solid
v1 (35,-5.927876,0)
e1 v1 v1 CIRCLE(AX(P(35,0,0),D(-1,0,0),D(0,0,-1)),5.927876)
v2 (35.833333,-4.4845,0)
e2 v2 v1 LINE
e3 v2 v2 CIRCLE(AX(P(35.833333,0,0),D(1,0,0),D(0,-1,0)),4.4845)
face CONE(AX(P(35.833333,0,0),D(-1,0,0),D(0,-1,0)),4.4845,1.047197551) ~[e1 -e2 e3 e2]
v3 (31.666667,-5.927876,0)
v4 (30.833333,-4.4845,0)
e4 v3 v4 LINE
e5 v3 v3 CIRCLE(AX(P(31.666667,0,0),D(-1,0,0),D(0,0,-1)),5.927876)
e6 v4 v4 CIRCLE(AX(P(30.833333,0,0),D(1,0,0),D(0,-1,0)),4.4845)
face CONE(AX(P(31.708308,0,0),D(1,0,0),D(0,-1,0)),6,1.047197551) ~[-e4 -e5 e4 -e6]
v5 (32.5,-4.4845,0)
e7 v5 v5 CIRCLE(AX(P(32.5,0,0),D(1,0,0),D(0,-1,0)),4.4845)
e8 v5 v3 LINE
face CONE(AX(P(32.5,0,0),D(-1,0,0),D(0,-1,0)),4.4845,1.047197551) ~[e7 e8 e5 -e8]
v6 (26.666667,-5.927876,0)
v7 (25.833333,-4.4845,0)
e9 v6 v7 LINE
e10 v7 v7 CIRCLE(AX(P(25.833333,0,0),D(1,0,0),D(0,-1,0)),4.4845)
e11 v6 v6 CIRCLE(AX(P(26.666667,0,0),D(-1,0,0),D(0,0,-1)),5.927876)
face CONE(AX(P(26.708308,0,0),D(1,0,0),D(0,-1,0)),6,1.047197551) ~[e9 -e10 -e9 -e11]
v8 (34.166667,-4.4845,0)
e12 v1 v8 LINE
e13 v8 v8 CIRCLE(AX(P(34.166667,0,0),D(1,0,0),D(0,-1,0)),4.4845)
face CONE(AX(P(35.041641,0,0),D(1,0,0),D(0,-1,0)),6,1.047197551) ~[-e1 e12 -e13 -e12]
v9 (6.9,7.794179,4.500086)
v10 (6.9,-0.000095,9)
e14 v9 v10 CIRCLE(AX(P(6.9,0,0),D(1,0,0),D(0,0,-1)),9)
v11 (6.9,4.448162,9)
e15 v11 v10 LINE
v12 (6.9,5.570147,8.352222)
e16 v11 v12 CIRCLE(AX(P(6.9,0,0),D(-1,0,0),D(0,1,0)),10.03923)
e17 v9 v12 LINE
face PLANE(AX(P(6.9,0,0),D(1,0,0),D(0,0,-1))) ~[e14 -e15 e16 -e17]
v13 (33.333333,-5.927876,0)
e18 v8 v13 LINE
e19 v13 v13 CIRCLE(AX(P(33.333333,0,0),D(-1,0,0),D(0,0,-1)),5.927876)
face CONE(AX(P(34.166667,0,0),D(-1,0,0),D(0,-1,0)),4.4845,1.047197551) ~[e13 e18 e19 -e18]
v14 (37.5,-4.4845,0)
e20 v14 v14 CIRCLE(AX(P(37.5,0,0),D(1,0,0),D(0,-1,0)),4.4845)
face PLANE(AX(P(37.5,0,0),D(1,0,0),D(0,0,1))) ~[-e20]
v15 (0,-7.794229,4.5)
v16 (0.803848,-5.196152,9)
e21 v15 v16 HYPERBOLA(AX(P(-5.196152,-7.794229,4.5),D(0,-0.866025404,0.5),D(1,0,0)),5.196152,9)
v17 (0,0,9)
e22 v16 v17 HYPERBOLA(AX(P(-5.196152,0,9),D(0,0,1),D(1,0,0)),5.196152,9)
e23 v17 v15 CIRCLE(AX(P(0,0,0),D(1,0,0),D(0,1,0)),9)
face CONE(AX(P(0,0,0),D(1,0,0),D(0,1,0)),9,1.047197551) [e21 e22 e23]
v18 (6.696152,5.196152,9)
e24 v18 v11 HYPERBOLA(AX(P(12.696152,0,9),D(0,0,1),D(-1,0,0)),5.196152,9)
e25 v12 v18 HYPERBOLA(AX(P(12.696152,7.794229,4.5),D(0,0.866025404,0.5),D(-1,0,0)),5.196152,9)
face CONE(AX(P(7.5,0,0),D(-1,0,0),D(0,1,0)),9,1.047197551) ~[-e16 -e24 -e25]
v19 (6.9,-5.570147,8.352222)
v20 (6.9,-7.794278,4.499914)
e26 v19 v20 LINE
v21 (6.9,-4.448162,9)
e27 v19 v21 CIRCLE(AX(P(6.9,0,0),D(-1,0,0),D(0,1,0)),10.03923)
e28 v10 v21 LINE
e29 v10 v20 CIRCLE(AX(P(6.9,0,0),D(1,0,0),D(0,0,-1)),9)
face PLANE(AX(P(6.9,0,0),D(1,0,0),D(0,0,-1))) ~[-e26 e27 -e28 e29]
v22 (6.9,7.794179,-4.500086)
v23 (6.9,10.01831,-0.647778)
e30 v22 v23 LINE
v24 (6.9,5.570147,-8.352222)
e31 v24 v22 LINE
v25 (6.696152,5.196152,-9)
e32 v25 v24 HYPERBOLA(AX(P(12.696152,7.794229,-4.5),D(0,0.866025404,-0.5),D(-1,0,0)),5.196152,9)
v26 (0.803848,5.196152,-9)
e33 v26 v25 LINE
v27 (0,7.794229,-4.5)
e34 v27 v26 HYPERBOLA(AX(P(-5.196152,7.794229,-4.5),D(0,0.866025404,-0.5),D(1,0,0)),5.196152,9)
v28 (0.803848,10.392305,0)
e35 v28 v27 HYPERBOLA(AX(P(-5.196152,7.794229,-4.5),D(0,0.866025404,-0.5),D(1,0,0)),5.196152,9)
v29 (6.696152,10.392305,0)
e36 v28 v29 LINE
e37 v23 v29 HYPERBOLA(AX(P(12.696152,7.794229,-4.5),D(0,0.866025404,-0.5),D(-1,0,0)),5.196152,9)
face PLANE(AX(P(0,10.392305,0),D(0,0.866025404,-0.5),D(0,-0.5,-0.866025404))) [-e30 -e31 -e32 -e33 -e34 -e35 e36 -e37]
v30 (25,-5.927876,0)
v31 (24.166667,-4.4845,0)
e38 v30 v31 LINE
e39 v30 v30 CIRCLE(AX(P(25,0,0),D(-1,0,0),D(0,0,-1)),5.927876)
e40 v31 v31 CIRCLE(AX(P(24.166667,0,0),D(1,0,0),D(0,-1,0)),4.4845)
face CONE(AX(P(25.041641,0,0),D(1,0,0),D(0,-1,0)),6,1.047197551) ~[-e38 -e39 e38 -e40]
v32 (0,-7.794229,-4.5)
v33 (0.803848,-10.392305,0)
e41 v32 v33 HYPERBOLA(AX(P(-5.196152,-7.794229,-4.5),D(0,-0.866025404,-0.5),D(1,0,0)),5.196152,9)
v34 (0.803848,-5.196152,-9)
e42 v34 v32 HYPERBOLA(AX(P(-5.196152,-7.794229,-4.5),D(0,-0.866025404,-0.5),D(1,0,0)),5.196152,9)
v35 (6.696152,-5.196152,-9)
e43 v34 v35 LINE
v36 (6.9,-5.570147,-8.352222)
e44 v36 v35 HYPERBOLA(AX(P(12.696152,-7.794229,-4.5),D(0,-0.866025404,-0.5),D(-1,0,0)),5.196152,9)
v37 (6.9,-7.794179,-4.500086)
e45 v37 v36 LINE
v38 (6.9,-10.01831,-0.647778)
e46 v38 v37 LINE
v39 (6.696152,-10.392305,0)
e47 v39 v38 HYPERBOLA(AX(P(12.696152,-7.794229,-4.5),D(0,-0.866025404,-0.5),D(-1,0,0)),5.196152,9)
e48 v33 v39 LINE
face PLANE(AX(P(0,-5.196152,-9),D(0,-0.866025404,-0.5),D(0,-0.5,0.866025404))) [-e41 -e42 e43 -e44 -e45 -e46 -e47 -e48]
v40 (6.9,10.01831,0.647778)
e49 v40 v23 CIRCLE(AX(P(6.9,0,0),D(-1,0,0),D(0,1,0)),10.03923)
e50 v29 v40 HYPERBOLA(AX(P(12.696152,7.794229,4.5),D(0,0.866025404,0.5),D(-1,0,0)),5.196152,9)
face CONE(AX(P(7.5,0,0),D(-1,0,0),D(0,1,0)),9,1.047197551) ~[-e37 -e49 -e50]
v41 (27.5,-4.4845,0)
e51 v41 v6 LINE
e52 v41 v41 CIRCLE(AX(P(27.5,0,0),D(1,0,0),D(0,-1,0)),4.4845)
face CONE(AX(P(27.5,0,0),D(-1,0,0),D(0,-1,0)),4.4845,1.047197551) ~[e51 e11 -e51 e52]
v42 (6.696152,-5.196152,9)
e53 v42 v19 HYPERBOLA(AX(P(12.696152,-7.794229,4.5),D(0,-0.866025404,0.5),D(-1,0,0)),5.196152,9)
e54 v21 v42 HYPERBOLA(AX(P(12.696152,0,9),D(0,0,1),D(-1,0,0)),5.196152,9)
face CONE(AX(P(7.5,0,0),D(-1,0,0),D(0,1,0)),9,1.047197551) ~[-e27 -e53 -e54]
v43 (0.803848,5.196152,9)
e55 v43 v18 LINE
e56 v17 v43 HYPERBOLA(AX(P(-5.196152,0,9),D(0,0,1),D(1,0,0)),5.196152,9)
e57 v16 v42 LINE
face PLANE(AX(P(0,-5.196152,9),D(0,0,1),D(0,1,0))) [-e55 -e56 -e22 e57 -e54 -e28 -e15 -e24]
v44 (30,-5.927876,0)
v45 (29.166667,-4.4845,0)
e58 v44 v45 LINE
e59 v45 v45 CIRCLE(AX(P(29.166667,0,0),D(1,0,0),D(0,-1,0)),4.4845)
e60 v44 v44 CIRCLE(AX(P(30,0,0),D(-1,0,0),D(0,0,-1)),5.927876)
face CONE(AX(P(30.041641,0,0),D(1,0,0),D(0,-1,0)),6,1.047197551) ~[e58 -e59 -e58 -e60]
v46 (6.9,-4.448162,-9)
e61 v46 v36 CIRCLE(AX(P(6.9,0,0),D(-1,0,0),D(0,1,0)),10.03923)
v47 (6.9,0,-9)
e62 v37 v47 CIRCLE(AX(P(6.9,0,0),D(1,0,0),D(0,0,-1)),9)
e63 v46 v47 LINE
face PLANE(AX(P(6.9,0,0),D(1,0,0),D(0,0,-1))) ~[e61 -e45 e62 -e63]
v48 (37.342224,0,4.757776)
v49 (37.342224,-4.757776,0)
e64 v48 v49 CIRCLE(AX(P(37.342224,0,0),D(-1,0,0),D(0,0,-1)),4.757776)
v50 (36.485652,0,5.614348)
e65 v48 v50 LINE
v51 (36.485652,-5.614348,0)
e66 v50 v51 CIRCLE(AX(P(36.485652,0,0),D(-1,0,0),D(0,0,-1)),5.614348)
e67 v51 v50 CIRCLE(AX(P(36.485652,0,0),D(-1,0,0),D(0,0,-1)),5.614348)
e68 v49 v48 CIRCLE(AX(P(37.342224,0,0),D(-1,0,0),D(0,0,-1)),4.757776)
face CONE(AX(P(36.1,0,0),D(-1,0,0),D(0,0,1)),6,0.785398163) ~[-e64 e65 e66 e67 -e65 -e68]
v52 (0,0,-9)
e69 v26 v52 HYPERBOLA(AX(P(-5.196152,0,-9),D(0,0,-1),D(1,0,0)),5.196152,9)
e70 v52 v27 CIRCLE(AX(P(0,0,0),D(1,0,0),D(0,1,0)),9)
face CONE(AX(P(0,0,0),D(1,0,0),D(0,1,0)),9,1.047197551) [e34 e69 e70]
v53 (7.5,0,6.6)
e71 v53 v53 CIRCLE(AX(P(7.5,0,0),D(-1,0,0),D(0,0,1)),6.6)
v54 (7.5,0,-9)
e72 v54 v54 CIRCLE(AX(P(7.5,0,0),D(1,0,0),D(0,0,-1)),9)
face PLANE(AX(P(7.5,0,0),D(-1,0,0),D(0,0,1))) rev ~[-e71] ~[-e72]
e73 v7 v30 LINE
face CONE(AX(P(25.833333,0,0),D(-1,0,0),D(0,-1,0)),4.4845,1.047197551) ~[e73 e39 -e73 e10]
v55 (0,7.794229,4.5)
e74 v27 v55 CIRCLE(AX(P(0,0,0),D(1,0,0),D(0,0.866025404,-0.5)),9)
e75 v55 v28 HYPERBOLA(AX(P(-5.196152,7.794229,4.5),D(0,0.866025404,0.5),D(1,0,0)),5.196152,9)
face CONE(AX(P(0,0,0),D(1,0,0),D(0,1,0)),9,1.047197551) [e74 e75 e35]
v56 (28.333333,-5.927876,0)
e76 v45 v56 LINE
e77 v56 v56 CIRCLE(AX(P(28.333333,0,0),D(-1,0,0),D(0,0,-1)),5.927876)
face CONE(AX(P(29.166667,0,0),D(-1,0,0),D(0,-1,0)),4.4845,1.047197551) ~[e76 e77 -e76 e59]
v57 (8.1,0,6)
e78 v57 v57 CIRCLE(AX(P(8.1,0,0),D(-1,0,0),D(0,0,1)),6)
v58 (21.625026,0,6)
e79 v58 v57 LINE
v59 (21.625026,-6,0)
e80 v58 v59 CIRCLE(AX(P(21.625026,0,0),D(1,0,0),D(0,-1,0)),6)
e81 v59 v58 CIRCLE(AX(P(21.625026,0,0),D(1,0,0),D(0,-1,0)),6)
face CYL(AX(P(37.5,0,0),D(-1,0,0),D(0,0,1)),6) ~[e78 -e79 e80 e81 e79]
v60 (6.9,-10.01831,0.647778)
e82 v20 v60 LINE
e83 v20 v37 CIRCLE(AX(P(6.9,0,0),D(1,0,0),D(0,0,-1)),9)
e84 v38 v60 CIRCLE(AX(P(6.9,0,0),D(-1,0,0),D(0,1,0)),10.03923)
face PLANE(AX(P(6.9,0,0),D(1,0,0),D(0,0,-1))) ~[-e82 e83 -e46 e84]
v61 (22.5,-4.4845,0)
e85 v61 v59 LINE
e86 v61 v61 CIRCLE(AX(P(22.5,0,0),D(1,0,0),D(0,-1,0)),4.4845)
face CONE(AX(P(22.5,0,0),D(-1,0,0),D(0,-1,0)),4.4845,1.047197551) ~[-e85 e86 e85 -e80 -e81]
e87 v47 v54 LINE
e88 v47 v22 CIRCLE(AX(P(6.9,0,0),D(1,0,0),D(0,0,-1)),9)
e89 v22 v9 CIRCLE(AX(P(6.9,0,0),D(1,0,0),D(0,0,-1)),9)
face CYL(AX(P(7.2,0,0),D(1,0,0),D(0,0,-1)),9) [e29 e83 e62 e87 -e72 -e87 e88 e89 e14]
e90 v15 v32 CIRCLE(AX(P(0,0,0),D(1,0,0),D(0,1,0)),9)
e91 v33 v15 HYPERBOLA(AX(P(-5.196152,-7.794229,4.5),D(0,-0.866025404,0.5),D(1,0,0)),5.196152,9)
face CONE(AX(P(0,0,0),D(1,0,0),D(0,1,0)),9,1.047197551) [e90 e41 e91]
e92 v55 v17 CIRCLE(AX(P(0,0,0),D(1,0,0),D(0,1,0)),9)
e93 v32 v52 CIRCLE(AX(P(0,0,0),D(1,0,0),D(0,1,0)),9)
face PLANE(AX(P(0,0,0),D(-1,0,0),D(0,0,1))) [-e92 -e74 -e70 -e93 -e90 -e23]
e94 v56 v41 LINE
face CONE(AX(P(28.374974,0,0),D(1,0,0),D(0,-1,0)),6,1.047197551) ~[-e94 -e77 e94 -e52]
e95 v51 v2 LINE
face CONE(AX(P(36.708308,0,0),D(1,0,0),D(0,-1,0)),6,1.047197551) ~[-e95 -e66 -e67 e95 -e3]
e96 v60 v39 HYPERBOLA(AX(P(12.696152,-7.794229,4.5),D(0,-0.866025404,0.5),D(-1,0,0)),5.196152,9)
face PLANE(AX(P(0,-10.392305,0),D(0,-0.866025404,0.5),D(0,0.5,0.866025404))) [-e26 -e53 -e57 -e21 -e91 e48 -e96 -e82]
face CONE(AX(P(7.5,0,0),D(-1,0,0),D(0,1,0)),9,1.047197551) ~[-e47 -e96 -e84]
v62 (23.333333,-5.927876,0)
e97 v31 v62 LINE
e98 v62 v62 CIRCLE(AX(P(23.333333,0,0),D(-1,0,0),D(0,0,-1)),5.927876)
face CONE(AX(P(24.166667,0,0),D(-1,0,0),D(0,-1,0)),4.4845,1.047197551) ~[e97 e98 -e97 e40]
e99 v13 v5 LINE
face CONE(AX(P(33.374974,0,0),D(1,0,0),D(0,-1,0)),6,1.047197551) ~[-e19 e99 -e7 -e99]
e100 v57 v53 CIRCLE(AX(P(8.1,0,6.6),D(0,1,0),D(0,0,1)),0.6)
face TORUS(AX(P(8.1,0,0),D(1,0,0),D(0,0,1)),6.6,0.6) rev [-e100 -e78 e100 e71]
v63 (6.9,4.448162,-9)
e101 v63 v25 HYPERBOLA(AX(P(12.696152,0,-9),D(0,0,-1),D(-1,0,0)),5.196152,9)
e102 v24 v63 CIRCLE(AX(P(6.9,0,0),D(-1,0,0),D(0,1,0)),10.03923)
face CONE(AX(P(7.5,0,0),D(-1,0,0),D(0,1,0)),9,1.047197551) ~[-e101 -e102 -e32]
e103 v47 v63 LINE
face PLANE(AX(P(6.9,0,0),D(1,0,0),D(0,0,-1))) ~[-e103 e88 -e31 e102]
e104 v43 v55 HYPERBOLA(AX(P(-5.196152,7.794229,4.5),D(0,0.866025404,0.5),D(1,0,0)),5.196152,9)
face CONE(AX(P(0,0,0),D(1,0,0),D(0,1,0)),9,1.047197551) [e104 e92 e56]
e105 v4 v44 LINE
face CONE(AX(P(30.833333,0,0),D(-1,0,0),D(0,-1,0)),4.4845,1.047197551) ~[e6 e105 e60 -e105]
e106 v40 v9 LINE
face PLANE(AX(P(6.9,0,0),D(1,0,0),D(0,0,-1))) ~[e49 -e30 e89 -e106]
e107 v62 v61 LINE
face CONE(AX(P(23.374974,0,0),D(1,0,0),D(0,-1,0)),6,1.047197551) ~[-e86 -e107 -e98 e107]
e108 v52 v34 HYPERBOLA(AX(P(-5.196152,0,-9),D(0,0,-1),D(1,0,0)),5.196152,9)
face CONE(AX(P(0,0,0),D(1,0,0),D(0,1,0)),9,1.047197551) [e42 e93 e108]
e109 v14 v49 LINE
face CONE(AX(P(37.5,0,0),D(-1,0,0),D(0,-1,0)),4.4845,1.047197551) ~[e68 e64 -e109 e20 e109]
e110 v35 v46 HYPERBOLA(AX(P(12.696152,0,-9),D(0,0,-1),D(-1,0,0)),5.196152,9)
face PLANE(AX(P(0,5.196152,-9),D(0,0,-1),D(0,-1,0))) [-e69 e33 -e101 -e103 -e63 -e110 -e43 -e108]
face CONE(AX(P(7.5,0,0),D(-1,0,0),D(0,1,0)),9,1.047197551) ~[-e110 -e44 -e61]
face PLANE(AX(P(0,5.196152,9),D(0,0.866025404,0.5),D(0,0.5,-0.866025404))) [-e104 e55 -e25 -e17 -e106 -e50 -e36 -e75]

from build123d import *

# Parameters (mm, degrees)
EXTRUDE_364_DEPTH      = 7.5
SKETCH_4_W             = 0.6
SKETCH_4_H             = 11.392304845
CHAMFER_2049_SIZE      = 1.4
FILLET_2094_R          = 0.6
PATTERN_LINEAR_1_COUNT = 10
PATTERN_LINEAR_1_PITCH = 1.666666667


with BuildPart() as part:
    # 草图1 → Extrude 364 (new body)
    with BuildSketch(Plane(origin=(0, 0, 0), x_dir=(0, 0, -1), z_dir=(1, 0, 0))):
        Polygon((9, 5.196152423), (9, -5.196152423), (0, -10.392304845), (-9, -5.196152423), (-9, 5.196152423), (0, 10.392304845), align=None)
    extrude(amount=EXTRUDE_364_DEPTH)

    # 草图2 → 凸台-旋转1 (revolve)
    with BuildSketch(Plane.XY, mode=Mode.PRIVATE) as revolve_1_sk:
        Polygon((0, 0), (37.5, 0), (37.5, 4.4845), (37.5, 6), (7.791693541, 6), (0, 6), align=None)
    revolve(revolve_1_sk.sketch.rotate(Axis((0, 0, 0), (1, 0, 0)), 90), axis=Axis((0, 0, 0), (1, 0, 0)))

    # 草图3 → 切除-旋转1 (revolve, cut)
    with BuildSketch(Plane.XY):
        Polygon((0, 9), (3.690598923, 15.392304845), (3.690598923, 20.392304845), (-10, 20.392304845), (-10, 9), align=None)
    revolve(axis=Axis((0, 0, 0), (1, 0, 0)), mode=Mode.SUBTRACT)

    # 草图5 → 切除-旋转2 (revolve, cut)
    with BuildSketch(Plane.XY):
        Polygon((7.5, 9), (3.809401077, 15.392304845), (3.809401077, 20.392304845), (13.809401077, 20.392304845), (13.809401077, 9), align=None)
    revolve(axis=Axis((0, 0, 0), (1, 0, 0)), mode=Mode.SUBTRACT)

    # 草图4 → 切除-旋转3 (revolve, cut)
    with BuildSketch(Plane.XY, mode=Mode.PRIVATE) as cut_revolve_3_sk:
        with Locations((7.2, 14.696152423)):
            Rectangle(SKETCH_4_W, SKETCH_4_H)
    revolve(cut_revolve_3_sk.sketch.rotate(Axis((0, 0, 0), (1, 0, 0)), 270), axis=Axis((0, 0, 0), (1, 0, 0)), mode=Mode.SUBTRACT)

    # Chamfer 2049
    chamfer_2049_edges = [part.edges().sort_by_distance(p)[0] for p in [
        (37.5, 0, -6),
    ]]
    chamfer(chamfer_2049_edges, length=CHAMFER_2049_SIZE)

    # Fillet 2094
    fillet_2094_edges = [part.edges().sort_by_distance(p)[0] for p in [
        (7.5, 0, -6),
    ]]
    fillet(fillet_2094_edges, radius=FILLET_2094_R)

    # 草图6 → 切除-旋转4 (revolve, cut)
    with BuildSketch(Plane.XY):
        Polygon((22.5, -4.4845), (21.625025667, -6), (21.625025667, -7.5), (23.374974333, -7.5), (23.374974333, -6), align=None)
    cut_revolve_4 = revolve(axis=Axis((-3.175, 0, 0), (1, 0, 0)), mode=Mode.SUBTRACT)

    # 阵列(线性)1: 切除-旋转4 ×10
    with Locations(*[(i * PATTERN_LINEAR_1_PITCH, 0, 0) for i in range(1, PATTERN_LINEAR_1_COUNT)]):
        add(cut_revolve_4, mode=Mode.SUBTRACT)


solid = part.part
